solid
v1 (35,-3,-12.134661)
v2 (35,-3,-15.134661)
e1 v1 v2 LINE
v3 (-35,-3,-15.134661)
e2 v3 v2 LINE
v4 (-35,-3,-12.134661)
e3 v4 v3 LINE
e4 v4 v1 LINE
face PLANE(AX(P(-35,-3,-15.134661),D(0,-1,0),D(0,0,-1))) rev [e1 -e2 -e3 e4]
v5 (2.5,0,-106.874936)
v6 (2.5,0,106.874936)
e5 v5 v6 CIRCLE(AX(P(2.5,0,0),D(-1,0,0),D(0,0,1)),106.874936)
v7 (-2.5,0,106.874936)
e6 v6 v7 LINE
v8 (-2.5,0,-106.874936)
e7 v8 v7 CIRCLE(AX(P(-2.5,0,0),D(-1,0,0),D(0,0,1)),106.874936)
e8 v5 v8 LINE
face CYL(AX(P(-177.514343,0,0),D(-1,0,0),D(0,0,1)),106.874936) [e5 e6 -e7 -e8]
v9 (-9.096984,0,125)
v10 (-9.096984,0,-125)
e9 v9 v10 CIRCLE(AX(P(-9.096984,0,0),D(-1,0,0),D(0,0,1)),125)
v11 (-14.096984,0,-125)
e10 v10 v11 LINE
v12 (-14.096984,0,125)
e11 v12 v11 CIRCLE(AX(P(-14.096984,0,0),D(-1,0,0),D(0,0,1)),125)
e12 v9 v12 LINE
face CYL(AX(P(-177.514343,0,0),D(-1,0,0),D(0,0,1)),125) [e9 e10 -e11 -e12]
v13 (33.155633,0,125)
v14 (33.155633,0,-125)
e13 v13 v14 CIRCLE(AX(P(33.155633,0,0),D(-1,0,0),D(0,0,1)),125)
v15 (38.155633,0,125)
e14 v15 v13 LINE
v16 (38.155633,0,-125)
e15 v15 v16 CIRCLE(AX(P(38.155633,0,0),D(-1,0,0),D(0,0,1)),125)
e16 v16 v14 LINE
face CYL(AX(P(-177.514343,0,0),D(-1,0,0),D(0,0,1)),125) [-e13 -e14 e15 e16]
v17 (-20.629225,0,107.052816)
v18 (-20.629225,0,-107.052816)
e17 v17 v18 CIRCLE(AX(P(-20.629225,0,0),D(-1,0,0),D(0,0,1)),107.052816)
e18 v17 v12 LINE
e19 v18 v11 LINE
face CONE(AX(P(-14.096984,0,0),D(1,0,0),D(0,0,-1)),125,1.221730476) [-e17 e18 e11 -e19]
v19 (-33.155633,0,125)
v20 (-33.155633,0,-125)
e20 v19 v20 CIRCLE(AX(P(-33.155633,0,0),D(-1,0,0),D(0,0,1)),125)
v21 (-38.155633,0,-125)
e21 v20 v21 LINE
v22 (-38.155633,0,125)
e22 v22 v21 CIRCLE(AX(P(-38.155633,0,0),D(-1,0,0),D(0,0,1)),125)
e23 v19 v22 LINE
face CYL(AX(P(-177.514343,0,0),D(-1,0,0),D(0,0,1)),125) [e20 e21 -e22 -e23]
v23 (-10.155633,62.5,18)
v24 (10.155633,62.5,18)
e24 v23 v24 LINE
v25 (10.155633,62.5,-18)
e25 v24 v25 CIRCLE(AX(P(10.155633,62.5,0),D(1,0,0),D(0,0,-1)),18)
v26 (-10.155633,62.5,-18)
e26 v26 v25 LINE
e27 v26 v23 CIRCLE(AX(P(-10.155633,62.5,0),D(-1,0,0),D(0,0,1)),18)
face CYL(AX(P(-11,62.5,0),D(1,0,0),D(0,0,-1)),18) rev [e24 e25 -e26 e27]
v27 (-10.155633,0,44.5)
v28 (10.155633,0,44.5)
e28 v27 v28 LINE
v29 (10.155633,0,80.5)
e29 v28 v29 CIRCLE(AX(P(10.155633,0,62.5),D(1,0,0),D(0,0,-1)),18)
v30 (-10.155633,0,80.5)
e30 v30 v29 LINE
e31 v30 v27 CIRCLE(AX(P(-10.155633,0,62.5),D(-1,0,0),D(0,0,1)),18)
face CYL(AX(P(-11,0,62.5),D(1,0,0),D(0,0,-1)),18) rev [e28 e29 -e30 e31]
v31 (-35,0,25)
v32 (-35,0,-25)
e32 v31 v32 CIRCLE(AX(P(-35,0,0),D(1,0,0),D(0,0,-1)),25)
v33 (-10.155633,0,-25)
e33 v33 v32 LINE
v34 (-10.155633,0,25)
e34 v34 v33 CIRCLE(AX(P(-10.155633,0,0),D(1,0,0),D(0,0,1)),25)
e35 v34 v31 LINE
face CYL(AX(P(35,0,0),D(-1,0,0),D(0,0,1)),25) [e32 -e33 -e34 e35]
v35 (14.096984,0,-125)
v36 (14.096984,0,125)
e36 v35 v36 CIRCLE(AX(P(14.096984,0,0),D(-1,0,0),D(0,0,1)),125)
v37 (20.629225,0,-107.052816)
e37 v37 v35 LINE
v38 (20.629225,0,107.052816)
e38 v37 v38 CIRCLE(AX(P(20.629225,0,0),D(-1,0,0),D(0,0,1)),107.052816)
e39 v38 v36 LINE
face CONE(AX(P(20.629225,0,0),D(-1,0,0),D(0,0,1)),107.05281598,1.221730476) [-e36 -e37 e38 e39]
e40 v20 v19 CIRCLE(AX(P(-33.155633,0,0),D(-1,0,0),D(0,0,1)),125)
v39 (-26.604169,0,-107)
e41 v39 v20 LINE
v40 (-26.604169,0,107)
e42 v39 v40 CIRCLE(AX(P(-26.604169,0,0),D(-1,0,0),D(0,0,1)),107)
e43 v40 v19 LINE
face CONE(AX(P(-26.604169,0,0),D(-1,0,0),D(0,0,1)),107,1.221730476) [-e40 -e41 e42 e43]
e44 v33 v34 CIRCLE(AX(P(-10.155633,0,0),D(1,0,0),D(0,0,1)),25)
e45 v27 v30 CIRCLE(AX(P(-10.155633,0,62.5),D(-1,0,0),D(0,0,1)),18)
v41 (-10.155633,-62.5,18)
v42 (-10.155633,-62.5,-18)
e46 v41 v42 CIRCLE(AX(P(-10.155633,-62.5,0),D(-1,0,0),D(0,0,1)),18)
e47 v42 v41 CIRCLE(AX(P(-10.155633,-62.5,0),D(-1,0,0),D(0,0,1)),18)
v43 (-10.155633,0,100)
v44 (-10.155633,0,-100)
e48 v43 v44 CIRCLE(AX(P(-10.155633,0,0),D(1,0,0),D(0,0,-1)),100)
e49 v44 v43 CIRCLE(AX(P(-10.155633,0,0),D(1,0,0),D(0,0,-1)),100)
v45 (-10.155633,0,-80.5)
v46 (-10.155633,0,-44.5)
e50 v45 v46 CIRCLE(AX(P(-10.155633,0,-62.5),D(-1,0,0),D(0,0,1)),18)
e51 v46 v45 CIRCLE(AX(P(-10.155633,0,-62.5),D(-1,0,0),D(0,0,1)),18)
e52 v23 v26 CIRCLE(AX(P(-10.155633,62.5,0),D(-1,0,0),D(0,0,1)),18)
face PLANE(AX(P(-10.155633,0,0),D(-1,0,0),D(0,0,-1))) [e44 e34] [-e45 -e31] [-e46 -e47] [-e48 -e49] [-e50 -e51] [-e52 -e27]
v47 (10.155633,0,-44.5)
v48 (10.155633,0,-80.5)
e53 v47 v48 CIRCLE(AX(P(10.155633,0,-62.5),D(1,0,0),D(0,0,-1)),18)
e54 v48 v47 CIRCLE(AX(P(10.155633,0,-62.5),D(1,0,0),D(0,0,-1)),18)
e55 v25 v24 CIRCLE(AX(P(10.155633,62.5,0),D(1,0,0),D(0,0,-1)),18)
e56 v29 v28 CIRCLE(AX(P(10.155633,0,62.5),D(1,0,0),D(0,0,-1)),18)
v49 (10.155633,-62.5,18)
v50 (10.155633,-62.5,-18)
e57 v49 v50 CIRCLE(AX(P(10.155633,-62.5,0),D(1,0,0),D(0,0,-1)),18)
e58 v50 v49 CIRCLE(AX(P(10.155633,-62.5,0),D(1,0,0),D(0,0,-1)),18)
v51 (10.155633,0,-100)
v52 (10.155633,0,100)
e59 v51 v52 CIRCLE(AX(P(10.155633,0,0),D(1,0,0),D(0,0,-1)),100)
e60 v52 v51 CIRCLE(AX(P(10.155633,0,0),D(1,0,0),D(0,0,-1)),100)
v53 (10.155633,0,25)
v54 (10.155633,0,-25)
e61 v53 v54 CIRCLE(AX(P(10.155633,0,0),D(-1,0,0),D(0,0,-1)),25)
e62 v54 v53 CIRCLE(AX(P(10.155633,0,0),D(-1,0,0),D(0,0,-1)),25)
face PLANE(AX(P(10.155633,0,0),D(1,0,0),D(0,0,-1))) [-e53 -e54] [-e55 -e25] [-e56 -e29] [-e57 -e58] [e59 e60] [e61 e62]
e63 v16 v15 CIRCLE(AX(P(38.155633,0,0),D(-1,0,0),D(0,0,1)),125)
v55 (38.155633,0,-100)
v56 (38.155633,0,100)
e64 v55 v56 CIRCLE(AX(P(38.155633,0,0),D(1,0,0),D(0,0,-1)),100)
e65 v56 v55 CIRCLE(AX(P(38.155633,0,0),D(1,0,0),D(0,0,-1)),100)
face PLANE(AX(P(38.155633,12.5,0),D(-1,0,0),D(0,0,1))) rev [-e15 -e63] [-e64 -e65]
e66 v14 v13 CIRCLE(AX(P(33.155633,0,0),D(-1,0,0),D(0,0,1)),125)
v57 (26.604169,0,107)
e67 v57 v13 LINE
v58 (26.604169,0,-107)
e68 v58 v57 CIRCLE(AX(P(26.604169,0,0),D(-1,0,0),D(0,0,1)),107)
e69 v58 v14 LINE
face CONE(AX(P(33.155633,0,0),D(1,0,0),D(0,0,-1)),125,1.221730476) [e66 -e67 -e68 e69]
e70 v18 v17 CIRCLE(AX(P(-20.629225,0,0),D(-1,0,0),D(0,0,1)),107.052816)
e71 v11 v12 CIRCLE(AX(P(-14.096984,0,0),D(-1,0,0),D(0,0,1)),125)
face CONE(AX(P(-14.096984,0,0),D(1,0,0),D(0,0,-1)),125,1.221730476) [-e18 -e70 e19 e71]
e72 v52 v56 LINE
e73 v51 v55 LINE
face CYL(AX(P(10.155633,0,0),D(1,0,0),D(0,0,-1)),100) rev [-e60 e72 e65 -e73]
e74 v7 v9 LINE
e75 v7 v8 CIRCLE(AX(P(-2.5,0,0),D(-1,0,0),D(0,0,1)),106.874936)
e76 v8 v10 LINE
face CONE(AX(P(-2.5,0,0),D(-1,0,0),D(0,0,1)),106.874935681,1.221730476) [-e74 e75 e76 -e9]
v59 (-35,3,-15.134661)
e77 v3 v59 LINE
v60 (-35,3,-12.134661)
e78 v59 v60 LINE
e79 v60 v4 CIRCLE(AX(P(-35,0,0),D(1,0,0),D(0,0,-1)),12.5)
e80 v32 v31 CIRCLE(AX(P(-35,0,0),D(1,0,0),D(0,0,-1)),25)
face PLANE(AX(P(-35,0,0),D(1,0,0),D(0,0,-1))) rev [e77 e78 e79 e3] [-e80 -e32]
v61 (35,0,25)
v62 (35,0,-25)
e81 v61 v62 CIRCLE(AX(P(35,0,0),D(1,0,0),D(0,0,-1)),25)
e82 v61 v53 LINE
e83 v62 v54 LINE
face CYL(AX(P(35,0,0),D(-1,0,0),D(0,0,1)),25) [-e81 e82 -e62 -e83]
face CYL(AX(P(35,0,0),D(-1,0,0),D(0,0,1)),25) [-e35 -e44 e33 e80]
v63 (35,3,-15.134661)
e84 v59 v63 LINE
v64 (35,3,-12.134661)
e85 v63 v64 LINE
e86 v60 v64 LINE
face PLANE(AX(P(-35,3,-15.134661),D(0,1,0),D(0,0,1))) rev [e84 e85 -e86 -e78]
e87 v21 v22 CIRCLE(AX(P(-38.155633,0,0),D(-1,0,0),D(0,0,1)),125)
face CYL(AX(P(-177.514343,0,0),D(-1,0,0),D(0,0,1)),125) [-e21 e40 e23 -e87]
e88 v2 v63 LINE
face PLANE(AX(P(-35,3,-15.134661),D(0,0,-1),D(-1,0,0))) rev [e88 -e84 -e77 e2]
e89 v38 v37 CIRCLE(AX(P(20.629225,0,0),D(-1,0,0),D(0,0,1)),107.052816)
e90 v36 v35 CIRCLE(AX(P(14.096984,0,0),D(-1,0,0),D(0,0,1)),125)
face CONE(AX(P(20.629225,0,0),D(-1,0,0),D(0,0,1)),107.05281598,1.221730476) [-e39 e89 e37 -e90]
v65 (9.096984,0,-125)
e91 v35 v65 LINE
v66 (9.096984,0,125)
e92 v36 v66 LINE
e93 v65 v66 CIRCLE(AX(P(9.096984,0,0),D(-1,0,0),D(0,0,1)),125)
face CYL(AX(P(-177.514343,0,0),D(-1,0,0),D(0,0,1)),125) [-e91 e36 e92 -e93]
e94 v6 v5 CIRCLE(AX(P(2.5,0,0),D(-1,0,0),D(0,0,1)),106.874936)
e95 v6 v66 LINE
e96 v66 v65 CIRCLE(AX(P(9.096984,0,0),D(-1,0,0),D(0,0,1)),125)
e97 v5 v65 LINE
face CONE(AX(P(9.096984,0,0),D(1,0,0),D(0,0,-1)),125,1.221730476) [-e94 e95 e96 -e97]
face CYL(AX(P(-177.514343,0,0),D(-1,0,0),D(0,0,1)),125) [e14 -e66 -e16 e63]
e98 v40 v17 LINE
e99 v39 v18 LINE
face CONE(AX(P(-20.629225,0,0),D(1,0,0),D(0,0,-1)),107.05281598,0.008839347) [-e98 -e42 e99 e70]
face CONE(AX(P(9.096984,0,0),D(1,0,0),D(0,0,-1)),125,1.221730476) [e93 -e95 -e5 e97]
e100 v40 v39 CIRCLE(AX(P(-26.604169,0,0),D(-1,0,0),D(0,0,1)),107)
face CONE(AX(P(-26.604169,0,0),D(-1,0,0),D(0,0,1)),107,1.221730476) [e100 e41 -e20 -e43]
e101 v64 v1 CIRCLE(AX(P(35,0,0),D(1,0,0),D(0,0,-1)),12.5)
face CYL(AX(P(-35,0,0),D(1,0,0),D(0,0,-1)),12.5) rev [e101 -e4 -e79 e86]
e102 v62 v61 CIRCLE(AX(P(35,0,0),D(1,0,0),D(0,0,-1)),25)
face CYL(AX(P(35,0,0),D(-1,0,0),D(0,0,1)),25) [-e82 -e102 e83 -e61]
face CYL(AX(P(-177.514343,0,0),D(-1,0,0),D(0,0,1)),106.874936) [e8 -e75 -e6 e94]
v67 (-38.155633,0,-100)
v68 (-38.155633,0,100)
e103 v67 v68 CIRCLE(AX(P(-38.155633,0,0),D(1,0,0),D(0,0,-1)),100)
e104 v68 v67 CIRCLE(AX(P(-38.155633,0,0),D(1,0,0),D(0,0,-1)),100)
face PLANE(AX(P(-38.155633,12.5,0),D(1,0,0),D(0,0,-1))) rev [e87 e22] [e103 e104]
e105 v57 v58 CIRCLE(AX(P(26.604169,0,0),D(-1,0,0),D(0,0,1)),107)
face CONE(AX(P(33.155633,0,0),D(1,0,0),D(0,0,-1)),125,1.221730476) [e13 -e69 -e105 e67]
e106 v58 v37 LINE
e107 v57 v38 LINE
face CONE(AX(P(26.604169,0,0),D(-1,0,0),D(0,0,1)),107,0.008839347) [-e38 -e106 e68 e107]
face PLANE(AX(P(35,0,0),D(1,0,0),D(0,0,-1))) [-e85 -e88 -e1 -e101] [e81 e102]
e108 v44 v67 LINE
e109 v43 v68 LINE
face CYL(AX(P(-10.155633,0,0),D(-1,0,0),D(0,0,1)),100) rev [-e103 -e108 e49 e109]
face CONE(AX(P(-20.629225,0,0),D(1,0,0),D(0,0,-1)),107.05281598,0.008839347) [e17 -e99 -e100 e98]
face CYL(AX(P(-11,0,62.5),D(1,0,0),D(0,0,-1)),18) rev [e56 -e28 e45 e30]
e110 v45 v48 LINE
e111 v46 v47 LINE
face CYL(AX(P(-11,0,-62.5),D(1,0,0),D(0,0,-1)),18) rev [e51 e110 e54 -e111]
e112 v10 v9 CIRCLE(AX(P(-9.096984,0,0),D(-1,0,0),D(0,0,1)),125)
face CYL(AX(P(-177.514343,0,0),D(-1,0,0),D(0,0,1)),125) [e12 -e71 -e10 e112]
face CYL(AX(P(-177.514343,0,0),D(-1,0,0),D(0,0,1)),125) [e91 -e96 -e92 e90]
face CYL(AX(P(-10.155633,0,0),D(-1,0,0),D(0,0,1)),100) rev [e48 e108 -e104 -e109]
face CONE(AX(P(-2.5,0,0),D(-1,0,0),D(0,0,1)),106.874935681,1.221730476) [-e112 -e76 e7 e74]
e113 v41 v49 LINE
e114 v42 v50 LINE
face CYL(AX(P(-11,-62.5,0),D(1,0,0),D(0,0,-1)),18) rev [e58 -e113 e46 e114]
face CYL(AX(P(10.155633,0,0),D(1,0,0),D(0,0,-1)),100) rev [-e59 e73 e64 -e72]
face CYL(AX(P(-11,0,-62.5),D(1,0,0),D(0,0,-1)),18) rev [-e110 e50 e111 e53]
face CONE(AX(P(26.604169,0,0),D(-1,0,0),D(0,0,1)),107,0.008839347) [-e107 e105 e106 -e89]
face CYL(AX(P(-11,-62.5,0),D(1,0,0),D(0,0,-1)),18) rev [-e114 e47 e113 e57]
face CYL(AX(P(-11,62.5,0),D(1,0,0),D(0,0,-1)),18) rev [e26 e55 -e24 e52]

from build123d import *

# Parameters (mm, degrees)
WEB_RECESS_SKETCH_R       = 100
WEB_RECESS_200_DEPTH      = 28
LIGHTENING_HOLES_SKETCH_R = 18
LIGHTENING_HOLES_4X_DEPTH = 11
HUB_SKETCH_R              = 25
HUB_50_DEPTH              = 35
BORE_SKETCH_R             = 12.5
BORE_25_DEPTH             = 35
KEYWAY_SKETCH_W           = 3
KEYWAY_SKETCH_H           = 6
KEYWAY_6X3_DEPTH          = 35


with BuildPart() as part:
    # Pulley Profile Sketch → Pulley Body 3-Groove (revolve)
    with BuildSketch(Plane.XY, mode=Mode.PRIVATE) as pulley_body_3_groove_sk:
        Polygon((-38.155633051, 12.5), (38.155633051, 12.5), (38.155633051, 125), (33.155633051, 125), (26.604168834, 107), (20.629224678, 107.05281598), (14.096983906, 125), (9.096983906, 125), (2.5, 106.874935681), (-2.5, 106.874935681), (-9.096983906, 125), (-14.096983906, 125), (-20.629224678, 107.05281598), (-26.604168834, 107), (-33.155633051, 125), (-38.155633051, 125), align=None)
    revolve(pulley_body_3_groove_sk.sketch.rotate(Axis((-177.514342584, 0, 0), (1, 0, 0)), 90), axis=Axis((-177.514342584, 0, 0), (1, 0, 0)))

    # Web Recess Sketch → Web Recess Ø200 (cut)
    with BuildSketch(Plane(origin=(38.155633051, 0, 0), x_dir=(0, 0, -1), z_dir=(1, 0, 0))):
        Circle(WEB_RECESS_SKETCH_R)
    web_recess_200 = extrude(amount=-WEB_RECESS_200_DEPTH, mode=Mode.SUBTRACT)

    # Web Recess Mirror: Web Recess Ø200 across plane
    add(web_recess_200.mirror(Plane(origin=(0, 0, 0), x_dir=(0, 0, 1), z_dir=(1, 0, 0))), mode=Mode.SUBTRACT)

    # Lightening Holes Sketch → Lightening Holes 4x (cut, symmetric)
    with BuildSketch(Plane(origin=(0, 0, 0), x_dir=(0, 0, -1), z_dir=(1, 0, 0))):
        with Locations((0, 62.5)):
            Circle(LIGHTENING_HOLES_SKETCH_R)
        with Locations((62.5, 0)):
            Circle(LIGHTENING_HOLES_SKETCH_R)
        with Locations((0, -62.5)):
            Circle(LIGHTENING_HOLES_SKETCH_R)
        with Locations((-62.5, 0)):
            Circle(LIGHTENING_HOLES_SKETCH_R)
    extrude(amount=LIGHTENING_HOLES_4X_DEPTH, both=True, mode=Mode.SUBTRACT)

    # Hub Sketch → Hub Ø50 (add, symmetric)
    with BuildSketch(Plane(origin=(0, 0, 0), x_dir=(0, 0, -1), z_dir=(1, 0, 0))):
        with Locations(Location((0, 0, 0), (0, 0, 180))):
            Circle(HUB_SKETCH_R)
    extrude(amount=HUB_50_DEPTH, both=True)

    # Bore Sketch → Bore Ø25 (cut, symmetric)
    with BuildSketch(Plane(origin=(0, 0, 0), x_dir=(0, 0, -1), z_dir=(1, 0, 0))):
        Circle(BORE_SKETCH_R)
    extrude(amount=BORE_25_DEPTH, both=True, mode=Mode.SUBTRACT)

    # Keyway Sketch → Keyway 6x3 (cut, symmetric)
    with BuildSketch(Plane(origin=(0, 0, 0), x_dir=(0, 0, -1), z_dir=(1, 0, 0))):
        with Locations((13.6346611, 0)):
            Rectangle(KEYWAY_SKETCH_W, KEYWAY_SKETCH_H)
    extrude(amount=KEYWAY_6X3_DEPTH, both=True, mode=Mode.SUBTRACT)


solid = part.part
